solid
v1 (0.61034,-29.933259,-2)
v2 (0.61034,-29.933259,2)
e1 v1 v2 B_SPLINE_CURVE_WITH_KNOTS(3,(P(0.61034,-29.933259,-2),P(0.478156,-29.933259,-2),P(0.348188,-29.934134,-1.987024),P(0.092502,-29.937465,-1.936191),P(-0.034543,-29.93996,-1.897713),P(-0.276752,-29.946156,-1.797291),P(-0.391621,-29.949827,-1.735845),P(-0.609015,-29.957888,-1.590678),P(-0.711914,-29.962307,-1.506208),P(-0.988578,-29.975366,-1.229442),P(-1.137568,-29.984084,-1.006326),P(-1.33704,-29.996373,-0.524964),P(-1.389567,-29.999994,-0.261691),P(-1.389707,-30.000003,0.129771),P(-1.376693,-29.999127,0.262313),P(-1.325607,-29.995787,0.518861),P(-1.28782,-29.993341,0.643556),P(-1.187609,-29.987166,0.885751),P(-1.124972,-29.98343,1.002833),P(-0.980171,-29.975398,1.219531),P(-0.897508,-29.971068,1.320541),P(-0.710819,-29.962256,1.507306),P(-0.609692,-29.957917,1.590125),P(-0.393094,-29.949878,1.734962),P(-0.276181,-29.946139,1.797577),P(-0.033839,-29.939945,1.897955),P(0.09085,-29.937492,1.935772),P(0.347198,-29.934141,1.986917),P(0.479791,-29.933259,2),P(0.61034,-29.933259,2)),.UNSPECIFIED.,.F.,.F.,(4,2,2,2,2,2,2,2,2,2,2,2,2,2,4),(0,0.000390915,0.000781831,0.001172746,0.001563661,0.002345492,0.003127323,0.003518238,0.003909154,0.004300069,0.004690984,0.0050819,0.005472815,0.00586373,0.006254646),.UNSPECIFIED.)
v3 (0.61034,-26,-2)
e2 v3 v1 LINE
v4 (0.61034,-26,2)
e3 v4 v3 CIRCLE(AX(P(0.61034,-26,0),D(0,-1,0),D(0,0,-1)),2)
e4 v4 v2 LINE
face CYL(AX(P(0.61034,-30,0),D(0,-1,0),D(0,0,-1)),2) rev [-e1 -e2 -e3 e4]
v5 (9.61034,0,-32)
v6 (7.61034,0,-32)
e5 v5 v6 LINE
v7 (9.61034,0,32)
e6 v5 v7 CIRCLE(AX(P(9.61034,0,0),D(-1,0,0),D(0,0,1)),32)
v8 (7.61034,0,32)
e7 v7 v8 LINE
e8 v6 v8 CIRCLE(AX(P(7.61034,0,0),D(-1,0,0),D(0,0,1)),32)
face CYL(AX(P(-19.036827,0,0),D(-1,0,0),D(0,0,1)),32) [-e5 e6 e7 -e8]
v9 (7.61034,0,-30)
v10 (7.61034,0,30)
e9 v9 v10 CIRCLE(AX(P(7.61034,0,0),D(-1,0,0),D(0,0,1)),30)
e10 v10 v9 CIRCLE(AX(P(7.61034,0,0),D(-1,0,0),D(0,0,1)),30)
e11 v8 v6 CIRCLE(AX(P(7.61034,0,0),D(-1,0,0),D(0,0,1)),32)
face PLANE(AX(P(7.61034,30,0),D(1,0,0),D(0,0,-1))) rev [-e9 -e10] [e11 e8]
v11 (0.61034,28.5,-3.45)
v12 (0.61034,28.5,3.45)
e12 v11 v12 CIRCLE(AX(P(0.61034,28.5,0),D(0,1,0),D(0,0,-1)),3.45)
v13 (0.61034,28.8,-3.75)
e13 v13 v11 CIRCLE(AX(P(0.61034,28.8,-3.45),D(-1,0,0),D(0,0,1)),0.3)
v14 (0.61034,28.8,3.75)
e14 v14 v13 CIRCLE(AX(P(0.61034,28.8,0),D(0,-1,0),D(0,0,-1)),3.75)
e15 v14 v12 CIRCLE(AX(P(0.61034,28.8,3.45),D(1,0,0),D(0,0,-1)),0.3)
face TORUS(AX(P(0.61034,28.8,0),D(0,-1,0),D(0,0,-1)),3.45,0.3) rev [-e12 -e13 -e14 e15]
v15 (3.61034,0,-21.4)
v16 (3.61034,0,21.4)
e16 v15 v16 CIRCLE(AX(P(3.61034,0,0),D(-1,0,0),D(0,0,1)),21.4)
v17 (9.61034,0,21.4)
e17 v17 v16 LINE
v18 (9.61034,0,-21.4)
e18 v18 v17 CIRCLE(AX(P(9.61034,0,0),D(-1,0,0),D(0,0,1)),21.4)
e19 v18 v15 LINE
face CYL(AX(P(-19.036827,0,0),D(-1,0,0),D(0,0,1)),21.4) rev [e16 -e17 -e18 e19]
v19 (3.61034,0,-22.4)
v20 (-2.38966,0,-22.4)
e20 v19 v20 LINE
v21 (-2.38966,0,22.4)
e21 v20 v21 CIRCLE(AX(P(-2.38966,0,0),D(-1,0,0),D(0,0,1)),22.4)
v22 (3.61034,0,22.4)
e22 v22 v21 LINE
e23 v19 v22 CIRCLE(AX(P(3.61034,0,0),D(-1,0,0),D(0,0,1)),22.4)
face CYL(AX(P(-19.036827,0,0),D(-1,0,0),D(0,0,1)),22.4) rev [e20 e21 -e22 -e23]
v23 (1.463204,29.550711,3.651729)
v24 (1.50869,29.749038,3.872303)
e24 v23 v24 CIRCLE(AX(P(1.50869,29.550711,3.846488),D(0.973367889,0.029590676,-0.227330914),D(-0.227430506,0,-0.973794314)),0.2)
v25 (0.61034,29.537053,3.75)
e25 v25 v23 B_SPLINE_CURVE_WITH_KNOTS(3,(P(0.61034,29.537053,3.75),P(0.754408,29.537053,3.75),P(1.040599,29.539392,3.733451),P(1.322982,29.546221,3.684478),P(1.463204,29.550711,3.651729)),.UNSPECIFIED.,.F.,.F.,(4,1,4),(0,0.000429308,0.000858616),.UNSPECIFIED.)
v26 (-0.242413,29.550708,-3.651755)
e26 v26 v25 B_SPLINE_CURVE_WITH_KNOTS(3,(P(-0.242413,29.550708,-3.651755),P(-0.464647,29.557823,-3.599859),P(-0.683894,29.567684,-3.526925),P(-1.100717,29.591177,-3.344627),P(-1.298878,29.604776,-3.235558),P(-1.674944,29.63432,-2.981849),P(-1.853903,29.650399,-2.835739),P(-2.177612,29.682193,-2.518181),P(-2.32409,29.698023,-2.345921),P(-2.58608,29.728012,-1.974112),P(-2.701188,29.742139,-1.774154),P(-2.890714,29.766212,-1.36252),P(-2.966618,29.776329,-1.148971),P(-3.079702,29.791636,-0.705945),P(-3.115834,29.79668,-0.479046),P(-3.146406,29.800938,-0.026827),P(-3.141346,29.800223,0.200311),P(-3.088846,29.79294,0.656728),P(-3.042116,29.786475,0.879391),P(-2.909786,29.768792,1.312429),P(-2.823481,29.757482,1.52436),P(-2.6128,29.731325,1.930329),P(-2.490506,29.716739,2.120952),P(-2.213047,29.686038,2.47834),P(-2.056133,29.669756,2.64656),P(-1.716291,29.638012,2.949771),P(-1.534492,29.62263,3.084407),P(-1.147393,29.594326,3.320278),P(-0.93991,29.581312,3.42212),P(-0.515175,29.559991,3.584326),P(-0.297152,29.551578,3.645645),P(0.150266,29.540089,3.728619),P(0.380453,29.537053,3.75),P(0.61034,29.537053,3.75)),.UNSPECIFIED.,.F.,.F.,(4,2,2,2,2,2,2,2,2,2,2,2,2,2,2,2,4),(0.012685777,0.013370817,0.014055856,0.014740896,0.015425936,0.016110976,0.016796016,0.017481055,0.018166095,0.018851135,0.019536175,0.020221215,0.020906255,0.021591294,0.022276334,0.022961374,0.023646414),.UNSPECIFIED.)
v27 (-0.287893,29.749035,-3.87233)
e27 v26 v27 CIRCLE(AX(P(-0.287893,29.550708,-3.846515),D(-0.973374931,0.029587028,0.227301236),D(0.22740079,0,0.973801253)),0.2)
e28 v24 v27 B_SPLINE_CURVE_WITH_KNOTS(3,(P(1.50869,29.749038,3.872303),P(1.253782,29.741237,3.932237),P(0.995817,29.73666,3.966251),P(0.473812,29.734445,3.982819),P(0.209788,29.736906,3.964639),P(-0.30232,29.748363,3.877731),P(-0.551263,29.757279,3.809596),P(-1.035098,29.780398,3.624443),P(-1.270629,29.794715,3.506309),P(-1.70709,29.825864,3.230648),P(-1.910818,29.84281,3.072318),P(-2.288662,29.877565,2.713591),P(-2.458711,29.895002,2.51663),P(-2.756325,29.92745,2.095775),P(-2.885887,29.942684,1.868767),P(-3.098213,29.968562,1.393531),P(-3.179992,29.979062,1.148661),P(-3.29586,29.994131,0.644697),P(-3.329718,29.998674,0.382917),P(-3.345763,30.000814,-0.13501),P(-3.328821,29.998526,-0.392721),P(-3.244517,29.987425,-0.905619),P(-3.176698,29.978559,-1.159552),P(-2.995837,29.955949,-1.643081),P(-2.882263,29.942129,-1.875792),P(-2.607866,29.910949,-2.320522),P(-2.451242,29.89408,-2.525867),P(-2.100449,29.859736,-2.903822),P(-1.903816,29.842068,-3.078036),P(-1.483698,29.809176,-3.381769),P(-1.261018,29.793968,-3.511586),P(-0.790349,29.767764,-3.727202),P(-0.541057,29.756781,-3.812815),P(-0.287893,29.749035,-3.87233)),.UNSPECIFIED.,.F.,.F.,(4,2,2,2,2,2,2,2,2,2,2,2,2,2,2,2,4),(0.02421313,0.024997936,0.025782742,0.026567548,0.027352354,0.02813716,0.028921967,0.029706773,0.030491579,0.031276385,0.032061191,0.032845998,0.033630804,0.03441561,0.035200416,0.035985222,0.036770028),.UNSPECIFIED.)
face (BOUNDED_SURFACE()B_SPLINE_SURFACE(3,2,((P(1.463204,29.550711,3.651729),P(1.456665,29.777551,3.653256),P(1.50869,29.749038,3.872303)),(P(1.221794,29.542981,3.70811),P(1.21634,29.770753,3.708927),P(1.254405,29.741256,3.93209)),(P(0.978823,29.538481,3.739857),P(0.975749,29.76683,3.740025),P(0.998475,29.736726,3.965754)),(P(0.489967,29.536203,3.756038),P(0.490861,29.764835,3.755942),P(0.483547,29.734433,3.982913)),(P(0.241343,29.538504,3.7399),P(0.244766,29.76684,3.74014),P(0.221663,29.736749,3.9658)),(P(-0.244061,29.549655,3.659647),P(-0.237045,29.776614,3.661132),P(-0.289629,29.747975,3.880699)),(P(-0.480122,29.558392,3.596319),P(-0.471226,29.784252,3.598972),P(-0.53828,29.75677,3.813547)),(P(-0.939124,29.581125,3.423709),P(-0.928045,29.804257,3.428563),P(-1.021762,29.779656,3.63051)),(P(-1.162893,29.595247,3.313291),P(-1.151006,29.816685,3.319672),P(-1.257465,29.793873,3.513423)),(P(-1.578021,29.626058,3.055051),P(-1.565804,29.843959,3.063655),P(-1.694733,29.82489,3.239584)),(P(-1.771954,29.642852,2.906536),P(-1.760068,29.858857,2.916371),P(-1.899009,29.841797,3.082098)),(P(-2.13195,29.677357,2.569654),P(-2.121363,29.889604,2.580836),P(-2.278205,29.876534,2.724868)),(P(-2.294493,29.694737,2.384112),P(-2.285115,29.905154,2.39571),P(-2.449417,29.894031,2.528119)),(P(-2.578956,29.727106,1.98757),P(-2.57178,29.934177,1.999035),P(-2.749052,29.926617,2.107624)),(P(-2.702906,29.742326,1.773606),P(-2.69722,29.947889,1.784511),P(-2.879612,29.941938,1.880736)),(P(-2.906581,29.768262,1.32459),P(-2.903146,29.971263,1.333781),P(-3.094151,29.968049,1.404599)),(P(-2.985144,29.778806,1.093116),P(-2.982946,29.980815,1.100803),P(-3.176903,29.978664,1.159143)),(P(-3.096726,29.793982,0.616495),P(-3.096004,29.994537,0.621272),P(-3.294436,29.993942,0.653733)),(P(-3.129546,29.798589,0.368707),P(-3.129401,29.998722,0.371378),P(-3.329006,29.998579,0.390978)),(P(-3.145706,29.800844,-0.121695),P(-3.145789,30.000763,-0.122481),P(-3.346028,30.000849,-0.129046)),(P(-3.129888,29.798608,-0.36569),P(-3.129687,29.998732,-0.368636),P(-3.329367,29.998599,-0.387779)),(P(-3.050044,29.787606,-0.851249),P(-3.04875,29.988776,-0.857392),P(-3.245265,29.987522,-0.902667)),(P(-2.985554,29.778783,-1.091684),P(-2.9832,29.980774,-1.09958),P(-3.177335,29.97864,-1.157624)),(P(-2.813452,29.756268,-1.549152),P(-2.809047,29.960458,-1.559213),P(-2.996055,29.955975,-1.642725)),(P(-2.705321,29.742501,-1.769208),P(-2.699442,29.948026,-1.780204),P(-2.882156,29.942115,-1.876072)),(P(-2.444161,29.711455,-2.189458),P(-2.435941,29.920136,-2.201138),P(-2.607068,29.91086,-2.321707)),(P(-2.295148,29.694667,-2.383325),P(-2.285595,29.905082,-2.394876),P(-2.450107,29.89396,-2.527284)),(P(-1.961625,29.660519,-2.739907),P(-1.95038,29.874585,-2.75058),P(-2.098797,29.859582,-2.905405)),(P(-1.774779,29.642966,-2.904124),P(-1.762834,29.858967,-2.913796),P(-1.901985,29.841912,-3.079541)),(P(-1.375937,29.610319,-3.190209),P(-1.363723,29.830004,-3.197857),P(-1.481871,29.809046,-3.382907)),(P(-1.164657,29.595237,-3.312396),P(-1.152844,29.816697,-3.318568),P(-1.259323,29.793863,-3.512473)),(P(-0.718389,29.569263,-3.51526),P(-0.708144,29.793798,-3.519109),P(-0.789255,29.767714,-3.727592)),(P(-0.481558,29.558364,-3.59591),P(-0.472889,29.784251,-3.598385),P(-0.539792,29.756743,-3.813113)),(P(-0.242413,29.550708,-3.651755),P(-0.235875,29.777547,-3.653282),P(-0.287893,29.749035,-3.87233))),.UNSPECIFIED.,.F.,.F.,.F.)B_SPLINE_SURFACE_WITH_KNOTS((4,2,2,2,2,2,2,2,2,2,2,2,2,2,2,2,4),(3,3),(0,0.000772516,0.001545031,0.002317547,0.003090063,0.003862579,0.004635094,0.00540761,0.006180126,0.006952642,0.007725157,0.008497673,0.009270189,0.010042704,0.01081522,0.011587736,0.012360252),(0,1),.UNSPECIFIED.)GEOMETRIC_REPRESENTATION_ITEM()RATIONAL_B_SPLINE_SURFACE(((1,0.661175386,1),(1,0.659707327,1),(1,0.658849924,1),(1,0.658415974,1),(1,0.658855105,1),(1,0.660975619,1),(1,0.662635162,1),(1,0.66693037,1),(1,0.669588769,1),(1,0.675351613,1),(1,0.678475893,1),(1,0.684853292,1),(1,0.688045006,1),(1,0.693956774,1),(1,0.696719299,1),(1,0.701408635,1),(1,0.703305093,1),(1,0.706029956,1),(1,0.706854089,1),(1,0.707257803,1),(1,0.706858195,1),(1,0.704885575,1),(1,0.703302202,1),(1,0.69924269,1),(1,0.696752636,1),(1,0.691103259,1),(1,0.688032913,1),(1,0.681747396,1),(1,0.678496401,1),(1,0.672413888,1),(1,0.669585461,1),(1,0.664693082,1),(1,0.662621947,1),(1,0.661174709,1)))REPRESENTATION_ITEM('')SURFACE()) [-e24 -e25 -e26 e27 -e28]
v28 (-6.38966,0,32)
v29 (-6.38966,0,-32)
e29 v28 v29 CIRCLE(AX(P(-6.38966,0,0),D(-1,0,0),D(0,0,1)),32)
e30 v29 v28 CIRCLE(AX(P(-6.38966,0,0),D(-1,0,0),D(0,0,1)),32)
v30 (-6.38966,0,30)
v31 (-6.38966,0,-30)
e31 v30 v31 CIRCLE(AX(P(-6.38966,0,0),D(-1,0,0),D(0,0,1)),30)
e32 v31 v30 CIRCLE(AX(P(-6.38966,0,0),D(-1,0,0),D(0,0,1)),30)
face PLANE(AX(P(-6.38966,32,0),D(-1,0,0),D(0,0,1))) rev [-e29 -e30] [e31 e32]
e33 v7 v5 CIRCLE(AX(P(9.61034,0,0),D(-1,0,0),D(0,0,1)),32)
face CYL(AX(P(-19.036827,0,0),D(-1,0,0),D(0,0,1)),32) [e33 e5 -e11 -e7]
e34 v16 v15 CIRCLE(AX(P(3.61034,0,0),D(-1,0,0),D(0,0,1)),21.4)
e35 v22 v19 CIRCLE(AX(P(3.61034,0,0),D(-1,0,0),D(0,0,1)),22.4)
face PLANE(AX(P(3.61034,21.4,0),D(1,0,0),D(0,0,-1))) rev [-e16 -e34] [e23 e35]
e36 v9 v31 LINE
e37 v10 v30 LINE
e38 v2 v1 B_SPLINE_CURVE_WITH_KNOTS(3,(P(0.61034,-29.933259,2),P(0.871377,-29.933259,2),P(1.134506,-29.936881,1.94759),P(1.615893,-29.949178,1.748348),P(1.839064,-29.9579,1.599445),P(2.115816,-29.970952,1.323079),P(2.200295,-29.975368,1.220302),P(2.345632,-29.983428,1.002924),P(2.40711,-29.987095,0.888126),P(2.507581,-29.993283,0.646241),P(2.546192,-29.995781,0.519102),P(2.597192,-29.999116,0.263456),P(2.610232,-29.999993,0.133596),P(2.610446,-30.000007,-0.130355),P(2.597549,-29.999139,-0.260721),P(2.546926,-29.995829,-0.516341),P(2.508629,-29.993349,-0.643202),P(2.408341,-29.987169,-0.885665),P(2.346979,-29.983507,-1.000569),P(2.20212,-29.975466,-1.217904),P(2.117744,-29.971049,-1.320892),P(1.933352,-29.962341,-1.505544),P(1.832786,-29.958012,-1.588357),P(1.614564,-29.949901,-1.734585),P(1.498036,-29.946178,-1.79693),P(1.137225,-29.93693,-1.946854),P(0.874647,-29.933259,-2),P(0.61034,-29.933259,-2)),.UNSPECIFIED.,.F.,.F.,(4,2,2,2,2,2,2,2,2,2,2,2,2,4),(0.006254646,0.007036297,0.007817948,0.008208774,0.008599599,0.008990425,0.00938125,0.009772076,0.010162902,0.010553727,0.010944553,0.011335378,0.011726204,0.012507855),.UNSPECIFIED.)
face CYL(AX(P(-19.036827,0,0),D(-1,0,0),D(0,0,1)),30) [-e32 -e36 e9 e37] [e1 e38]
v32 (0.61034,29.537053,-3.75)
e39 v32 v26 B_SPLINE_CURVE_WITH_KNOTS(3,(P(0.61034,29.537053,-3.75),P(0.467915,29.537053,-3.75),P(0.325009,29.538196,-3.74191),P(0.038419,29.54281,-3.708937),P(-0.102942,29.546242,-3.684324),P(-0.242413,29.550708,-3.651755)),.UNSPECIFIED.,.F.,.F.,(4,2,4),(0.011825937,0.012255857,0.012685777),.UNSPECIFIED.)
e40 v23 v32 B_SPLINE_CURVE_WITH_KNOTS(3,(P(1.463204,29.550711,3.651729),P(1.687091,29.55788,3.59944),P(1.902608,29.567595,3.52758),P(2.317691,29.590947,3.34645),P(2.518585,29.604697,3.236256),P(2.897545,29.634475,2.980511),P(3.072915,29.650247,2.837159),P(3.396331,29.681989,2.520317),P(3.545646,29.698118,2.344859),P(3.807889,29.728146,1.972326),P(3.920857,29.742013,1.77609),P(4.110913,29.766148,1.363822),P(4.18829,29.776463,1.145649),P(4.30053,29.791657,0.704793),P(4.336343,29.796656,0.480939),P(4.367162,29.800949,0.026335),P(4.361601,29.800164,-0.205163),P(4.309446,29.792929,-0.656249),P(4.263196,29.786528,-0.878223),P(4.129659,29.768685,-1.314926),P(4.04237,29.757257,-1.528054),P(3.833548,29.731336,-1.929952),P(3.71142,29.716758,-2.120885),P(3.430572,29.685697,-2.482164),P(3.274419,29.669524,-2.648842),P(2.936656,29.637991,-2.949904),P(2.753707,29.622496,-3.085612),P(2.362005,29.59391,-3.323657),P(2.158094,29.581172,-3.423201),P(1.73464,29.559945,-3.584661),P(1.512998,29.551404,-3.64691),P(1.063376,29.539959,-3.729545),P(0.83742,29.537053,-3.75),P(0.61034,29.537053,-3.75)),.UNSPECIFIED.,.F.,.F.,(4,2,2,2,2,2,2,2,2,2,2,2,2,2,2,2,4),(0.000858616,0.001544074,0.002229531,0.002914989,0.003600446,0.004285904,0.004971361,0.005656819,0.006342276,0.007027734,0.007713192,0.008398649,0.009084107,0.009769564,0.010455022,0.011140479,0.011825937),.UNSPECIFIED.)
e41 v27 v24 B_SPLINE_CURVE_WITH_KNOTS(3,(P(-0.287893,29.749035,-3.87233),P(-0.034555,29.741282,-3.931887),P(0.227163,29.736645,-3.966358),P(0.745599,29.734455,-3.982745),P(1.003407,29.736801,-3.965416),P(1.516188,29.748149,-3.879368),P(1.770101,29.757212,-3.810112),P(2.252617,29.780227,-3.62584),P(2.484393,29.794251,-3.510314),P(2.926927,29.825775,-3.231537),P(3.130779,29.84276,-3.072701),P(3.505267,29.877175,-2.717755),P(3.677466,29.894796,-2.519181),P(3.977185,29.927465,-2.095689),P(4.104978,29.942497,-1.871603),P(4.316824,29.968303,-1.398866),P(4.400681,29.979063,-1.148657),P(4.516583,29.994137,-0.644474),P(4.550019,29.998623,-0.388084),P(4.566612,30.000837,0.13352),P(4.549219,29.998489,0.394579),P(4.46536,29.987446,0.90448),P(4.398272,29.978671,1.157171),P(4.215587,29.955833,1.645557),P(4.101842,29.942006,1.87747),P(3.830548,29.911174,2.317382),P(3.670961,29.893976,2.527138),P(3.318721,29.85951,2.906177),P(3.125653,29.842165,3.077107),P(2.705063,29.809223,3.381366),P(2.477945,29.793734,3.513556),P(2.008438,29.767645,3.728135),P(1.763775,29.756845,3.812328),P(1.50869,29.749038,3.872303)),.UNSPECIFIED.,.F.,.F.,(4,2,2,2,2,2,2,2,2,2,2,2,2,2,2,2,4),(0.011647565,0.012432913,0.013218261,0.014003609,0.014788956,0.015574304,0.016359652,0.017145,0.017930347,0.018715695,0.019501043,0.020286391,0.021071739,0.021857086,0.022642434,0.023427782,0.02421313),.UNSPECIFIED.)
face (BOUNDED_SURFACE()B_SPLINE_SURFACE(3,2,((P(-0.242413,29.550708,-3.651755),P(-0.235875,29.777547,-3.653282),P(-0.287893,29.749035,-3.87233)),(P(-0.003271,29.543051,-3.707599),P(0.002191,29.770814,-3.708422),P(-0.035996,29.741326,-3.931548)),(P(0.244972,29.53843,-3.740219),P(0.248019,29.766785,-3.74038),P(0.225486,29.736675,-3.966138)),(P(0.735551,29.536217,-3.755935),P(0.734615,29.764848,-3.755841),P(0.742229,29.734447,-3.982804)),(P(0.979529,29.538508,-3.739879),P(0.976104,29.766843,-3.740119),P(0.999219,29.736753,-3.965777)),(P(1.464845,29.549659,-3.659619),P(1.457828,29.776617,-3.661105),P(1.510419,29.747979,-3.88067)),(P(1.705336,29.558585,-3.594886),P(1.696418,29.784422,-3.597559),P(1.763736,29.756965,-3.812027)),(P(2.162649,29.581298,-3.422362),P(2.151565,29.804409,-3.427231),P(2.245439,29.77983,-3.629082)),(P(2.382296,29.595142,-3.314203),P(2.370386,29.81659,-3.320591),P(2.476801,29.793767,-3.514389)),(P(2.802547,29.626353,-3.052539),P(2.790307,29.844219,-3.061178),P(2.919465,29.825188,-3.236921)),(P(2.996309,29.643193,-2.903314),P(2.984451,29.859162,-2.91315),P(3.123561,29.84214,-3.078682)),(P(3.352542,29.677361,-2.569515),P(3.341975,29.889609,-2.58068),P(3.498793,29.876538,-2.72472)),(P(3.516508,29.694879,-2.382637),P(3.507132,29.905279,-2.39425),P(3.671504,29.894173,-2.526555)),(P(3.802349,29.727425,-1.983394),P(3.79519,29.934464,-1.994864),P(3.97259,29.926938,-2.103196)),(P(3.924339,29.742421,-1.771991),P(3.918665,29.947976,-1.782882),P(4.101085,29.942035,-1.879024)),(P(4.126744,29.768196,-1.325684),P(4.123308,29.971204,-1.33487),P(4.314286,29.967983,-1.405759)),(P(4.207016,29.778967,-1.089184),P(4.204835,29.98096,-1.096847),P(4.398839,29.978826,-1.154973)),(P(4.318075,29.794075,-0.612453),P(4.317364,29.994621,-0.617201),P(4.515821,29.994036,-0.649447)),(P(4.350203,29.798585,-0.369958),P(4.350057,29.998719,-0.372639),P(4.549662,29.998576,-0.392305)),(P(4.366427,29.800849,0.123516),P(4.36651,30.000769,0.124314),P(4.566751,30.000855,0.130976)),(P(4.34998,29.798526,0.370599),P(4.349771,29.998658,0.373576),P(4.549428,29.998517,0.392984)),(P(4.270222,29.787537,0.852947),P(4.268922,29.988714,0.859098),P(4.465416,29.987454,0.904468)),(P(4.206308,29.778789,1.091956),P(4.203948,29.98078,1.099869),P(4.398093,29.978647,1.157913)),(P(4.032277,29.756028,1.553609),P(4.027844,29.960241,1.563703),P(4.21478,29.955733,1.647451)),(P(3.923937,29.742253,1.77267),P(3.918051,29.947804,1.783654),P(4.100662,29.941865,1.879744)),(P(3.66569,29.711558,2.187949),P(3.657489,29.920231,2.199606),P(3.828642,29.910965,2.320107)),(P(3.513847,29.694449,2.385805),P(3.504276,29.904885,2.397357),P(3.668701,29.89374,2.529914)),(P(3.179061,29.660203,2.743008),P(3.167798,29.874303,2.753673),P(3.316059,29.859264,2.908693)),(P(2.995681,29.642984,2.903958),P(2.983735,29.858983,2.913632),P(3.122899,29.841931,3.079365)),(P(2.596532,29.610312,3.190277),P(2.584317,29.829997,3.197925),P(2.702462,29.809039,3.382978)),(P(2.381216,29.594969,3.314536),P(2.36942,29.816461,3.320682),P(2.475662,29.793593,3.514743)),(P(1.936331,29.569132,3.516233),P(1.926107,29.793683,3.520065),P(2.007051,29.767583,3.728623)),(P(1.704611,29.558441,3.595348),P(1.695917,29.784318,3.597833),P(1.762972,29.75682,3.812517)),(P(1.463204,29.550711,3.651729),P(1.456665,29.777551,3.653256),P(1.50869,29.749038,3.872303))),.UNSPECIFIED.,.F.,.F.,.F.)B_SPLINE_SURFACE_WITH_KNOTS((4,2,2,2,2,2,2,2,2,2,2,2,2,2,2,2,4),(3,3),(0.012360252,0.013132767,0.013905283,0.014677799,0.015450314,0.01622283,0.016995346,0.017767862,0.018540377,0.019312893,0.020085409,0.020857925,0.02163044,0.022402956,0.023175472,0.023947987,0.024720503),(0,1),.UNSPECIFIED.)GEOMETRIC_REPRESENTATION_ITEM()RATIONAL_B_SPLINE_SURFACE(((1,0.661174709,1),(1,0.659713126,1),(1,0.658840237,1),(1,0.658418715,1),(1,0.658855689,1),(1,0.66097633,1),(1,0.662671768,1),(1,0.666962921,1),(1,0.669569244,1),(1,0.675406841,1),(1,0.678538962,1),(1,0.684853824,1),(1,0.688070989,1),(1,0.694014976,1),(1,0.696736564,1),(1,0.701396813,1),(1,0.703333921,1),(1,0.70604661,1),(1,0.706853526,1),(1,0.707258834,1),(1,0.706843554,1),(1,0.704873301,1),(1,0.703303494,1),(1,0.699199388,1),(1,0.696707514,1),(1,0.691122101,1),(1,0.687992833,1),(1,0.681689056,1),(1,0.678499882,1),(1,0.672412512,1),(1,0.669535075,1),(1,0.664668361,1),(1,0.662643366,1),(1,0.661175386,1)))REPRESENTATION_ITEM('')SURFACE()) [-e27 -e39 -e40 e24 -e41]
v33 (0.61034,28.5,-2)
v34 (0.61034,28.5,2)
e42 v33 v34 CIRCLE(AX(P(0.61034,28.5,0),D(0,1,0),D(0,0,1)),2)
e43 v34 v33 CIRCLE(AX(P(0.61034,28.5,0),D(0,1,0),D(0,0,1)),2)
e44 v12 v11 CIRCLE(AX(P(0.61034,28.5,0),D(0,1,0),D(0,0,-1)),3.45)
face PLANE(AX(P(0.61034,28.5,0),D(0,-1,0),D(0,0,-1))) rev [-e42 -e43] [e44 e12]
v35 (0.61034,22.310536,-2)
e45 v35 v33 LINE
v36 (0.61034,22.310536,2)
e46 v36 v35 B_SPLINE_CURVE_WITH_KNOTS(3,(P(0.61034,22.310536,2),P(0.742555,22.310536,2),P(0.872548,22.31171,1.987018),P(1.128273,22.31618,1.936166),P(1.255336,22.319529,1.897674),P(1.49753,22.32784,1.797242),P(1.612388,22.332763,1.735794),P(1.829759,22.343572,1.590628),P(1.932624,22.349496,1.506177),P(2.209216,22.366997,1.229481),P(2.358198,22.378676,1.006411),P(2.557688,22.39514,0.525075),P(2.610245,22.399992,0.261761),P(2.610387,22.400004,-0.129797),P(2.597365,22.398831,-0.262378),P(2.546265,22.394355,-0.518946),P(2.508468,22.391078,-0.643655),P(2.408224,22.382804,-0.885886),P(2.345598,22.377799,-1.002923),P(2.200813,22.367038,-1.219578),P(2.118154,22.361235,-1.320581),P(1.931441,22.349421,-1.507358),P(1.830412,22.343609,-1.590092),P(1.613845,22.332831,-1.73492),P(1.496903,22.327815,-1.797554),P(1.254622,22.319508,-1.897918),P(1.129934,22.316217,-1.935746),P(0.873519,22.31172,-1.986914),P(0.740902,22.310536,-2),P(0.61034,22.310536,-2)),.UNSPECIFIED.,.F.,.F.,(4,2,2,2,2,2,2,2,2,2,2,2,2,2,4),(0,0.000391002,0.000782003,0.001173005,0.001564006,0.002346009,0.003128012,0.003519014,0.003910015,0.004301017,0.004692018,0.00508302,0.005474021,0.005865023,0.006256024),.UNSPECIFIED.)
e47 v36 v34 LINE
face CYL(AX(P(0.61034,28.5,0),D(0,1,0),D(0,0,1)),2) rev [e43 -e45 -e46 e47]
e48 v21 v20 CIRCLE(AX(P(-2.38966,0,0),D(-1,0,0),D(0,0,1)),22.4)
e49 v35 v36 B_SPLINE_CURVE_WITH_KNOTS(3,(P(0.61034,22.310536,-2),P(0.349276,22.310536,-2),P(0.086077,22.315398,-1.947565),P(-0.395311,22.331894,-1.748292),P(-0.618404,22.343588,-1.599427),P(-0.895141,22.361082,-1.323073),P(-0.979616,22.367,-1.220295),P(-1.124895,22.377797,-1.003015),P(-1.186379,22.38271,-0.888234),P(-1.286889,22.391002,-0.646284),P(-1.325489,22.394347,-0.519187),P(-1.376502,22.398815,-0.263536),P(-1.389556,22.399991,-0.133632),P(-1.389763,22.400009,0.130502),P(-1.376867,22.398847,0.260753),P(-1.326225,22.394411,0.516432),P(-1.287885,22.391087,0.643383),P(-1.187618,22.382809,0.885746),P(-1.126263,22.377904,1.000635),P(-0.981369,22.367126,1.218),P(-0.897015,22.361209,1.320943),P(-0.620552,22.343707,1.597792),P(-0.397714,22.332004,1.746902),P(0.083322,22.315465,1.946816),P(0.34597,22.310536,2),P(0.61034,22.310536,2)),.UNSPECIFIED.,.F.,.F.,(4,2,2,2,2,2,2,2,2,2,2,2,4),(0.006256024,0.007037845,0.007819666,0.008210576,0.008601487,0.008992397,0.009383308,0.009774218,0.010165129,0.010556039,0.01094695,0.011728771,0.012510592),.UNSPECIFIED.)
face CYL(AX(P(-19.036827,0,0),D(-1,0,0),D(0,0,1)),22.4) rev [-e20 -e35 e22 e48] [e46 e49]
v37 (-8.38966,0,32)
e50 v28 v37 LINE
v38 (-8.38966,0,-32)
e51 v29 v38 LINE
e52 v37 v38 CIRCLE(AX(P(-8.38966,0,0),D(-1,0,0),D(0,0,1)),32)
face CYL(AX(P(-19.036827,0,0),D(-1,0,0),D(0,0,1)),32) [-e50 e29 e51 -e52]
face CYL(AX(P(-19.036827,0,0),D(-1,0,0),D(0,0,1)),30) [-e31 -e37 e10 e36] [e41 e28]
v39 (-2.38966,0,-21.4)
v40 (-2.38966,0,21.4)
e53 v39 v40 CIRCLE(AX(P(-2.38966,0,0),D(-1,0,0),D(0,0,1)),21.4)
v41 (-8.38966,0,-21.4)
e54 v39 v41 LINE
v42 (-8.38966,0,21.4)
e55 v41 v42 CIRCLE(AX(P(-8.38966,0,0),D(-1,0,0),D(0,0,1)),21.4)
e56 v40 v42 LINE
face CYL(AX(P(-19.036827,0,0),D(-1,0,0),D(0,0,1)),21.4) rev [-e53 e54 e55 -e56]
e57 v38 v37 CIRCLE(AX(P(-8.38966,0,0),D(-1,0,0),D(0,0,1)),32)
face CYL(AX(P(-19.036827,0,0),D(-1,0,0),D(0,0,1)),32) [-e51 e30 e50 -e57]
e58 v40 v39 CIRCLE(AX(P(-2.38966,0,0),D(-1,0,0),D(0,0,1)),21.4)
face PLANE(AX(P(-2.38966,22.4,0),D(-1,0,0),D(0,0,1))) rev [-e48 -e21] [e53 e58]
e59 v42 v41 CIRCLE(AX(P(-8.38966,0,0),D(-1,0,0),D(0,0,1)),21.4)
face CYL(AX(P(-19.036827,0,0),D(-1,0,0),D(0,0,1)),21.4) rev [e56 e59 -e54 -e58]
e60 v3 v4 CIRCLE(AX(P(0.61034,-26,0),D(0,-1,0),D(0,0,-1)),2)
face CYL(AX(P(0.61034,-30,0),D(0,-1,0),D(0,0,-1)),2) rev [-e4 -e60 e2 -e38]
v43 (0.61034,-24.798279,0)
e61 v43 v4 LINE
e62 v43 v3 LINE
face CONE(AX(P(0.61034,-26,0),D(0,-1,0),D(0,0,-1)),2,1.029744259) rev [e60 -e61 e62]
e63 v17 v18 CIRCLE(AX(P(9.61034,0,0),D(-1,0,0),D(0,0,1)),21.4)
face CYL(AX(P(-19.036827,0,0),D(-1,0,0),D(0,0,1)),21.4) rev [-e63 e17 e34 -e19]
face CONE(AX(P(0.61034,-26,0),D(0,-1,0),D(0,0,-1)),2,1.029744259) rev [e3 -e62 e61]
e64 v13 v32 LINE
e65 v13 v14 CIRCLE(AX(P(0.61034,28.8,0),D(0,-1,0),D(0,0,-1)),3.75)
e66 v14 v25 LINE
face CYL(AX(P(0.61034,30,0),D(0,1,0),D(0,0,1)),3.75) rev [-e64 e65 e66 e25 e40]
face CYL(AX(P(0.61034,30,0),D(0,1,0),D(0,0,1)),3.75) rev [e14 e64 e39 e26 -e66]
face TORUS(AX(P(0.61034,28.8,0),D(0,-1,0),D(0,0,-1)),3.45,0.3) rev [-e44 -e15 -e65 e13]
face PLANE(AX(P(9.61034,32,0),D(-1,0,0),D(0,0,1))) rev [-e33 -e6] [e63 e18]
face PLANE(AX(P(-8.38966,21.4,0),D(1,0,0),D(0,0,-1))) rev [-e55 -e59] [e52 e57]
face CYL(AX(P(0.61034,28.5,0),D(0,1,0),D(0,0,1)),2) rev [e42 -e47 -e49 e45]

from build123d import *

# Parameters (mm, degrees)
HOLE1_D           = 7.5
HOLE1_DEPTH       = 1.5
HOLE2_REACH       = 71.113
HOLE2_BORE_R      = 2
DOWEL_HOLE1_D     = 4
DOWEL_HOLE1_DEPTH = 4
DOWEL_HOLE1_TIP   = 1.201721238
FILLET1_R         = 0.2
FILLET2_R         = 0.3


with BuildPart() as part:
    # Sketch1 → Revolve1 (revolve)
    with BuildSketch(Plane.XY, mode=Mode.PRIVATE) as revolve1_sk:
        Polygon((-8.389660143, 21.4), (-8.389660143, 32), (-6.389660143, 32), (-6.389660143, 30), (7.610339857, 30), (7.610339857, 32), (9.610339857, 32), (9.610339857, 21.4), (3.610339857, 21.4), (3.610339857, 22.4), (-2.389660143, 22.4), (-2.389660143, 21.4), align=None)
    revolve(revolve1_sk.sketch.rotate(Axis((-19.036826505, 0, 0), (1, 0, 0)), 90), axis=Axis((-19.036826505, 0, 0), (1, 0, 0)))

    # Hole1
    with Locations(Plane(origin=(0, 30, 0), x_dir=(1, 0, 0), z_dir=(0, 1, 0))):
        with Locations((0.610339857, 0)):
            Hole(HOLE1_D / 2, depth=HOLE1_DEPTH)

    # Hole2 bore → Hole2 (cut, up to next)
    with BuildSketch(Plane(origin=(0, 28.5, 0), x_dir=(1, 0, 0), z_dir=(0, 1, 0)), mode=Mode.PRIVATE) as hole2_sk1:
        with Locations((0.610339857, 0)):
            Circle(HOLE2_BORE_R)
    hole2_tool1 = extrude(hole2_sk1.sketch, amount=-HOLE2_REACH, mode=Mode.PRIVATE) & part.part
    add(hole2_tool1.solids().sort_by_distance((0.61034, 28.5, 0))[0], mode=Mode.SUBTRACT)

    # Dowel Hole1
    with Locations(Plane(origin=(0, -30, 0), x_dir=(-1, 0, 0), z_dir=(0, -1, 0))):
        with Locations((-0.610339857, 0)):
            Hole(DOWEL_HOLE1_D / 2, depth=DOWEL_HOLE1_DEPTH)
            with Locations((0, 0, -(DOWEL_HOLE1_DEPTH + DOWEL_HOLE1_TIP / 2))):  # 118° drill point
                Cone(0, DOWEL_HOLE1_D / 2, DOWEL_HOLE1_TIP, mode=Mode.SUBTRACT)

    # Fillet1
    fillet1_edges = [part.edges().sort_by_distance(p)[0] for p in [
        (4.360339864, 29.999999997, -1e-09),
    ]]
    fillet(fillet1_edges, radius=FILLET1_R)

    # Fillet2
    fillet2_edges = [part.edges().sort_by_distance(p)[0] for p in [
        (4.360339857, 28.5, 0),
    ]]
    fillet(fillet2_edges, radius=FILLET2_R)


solid = part.part
